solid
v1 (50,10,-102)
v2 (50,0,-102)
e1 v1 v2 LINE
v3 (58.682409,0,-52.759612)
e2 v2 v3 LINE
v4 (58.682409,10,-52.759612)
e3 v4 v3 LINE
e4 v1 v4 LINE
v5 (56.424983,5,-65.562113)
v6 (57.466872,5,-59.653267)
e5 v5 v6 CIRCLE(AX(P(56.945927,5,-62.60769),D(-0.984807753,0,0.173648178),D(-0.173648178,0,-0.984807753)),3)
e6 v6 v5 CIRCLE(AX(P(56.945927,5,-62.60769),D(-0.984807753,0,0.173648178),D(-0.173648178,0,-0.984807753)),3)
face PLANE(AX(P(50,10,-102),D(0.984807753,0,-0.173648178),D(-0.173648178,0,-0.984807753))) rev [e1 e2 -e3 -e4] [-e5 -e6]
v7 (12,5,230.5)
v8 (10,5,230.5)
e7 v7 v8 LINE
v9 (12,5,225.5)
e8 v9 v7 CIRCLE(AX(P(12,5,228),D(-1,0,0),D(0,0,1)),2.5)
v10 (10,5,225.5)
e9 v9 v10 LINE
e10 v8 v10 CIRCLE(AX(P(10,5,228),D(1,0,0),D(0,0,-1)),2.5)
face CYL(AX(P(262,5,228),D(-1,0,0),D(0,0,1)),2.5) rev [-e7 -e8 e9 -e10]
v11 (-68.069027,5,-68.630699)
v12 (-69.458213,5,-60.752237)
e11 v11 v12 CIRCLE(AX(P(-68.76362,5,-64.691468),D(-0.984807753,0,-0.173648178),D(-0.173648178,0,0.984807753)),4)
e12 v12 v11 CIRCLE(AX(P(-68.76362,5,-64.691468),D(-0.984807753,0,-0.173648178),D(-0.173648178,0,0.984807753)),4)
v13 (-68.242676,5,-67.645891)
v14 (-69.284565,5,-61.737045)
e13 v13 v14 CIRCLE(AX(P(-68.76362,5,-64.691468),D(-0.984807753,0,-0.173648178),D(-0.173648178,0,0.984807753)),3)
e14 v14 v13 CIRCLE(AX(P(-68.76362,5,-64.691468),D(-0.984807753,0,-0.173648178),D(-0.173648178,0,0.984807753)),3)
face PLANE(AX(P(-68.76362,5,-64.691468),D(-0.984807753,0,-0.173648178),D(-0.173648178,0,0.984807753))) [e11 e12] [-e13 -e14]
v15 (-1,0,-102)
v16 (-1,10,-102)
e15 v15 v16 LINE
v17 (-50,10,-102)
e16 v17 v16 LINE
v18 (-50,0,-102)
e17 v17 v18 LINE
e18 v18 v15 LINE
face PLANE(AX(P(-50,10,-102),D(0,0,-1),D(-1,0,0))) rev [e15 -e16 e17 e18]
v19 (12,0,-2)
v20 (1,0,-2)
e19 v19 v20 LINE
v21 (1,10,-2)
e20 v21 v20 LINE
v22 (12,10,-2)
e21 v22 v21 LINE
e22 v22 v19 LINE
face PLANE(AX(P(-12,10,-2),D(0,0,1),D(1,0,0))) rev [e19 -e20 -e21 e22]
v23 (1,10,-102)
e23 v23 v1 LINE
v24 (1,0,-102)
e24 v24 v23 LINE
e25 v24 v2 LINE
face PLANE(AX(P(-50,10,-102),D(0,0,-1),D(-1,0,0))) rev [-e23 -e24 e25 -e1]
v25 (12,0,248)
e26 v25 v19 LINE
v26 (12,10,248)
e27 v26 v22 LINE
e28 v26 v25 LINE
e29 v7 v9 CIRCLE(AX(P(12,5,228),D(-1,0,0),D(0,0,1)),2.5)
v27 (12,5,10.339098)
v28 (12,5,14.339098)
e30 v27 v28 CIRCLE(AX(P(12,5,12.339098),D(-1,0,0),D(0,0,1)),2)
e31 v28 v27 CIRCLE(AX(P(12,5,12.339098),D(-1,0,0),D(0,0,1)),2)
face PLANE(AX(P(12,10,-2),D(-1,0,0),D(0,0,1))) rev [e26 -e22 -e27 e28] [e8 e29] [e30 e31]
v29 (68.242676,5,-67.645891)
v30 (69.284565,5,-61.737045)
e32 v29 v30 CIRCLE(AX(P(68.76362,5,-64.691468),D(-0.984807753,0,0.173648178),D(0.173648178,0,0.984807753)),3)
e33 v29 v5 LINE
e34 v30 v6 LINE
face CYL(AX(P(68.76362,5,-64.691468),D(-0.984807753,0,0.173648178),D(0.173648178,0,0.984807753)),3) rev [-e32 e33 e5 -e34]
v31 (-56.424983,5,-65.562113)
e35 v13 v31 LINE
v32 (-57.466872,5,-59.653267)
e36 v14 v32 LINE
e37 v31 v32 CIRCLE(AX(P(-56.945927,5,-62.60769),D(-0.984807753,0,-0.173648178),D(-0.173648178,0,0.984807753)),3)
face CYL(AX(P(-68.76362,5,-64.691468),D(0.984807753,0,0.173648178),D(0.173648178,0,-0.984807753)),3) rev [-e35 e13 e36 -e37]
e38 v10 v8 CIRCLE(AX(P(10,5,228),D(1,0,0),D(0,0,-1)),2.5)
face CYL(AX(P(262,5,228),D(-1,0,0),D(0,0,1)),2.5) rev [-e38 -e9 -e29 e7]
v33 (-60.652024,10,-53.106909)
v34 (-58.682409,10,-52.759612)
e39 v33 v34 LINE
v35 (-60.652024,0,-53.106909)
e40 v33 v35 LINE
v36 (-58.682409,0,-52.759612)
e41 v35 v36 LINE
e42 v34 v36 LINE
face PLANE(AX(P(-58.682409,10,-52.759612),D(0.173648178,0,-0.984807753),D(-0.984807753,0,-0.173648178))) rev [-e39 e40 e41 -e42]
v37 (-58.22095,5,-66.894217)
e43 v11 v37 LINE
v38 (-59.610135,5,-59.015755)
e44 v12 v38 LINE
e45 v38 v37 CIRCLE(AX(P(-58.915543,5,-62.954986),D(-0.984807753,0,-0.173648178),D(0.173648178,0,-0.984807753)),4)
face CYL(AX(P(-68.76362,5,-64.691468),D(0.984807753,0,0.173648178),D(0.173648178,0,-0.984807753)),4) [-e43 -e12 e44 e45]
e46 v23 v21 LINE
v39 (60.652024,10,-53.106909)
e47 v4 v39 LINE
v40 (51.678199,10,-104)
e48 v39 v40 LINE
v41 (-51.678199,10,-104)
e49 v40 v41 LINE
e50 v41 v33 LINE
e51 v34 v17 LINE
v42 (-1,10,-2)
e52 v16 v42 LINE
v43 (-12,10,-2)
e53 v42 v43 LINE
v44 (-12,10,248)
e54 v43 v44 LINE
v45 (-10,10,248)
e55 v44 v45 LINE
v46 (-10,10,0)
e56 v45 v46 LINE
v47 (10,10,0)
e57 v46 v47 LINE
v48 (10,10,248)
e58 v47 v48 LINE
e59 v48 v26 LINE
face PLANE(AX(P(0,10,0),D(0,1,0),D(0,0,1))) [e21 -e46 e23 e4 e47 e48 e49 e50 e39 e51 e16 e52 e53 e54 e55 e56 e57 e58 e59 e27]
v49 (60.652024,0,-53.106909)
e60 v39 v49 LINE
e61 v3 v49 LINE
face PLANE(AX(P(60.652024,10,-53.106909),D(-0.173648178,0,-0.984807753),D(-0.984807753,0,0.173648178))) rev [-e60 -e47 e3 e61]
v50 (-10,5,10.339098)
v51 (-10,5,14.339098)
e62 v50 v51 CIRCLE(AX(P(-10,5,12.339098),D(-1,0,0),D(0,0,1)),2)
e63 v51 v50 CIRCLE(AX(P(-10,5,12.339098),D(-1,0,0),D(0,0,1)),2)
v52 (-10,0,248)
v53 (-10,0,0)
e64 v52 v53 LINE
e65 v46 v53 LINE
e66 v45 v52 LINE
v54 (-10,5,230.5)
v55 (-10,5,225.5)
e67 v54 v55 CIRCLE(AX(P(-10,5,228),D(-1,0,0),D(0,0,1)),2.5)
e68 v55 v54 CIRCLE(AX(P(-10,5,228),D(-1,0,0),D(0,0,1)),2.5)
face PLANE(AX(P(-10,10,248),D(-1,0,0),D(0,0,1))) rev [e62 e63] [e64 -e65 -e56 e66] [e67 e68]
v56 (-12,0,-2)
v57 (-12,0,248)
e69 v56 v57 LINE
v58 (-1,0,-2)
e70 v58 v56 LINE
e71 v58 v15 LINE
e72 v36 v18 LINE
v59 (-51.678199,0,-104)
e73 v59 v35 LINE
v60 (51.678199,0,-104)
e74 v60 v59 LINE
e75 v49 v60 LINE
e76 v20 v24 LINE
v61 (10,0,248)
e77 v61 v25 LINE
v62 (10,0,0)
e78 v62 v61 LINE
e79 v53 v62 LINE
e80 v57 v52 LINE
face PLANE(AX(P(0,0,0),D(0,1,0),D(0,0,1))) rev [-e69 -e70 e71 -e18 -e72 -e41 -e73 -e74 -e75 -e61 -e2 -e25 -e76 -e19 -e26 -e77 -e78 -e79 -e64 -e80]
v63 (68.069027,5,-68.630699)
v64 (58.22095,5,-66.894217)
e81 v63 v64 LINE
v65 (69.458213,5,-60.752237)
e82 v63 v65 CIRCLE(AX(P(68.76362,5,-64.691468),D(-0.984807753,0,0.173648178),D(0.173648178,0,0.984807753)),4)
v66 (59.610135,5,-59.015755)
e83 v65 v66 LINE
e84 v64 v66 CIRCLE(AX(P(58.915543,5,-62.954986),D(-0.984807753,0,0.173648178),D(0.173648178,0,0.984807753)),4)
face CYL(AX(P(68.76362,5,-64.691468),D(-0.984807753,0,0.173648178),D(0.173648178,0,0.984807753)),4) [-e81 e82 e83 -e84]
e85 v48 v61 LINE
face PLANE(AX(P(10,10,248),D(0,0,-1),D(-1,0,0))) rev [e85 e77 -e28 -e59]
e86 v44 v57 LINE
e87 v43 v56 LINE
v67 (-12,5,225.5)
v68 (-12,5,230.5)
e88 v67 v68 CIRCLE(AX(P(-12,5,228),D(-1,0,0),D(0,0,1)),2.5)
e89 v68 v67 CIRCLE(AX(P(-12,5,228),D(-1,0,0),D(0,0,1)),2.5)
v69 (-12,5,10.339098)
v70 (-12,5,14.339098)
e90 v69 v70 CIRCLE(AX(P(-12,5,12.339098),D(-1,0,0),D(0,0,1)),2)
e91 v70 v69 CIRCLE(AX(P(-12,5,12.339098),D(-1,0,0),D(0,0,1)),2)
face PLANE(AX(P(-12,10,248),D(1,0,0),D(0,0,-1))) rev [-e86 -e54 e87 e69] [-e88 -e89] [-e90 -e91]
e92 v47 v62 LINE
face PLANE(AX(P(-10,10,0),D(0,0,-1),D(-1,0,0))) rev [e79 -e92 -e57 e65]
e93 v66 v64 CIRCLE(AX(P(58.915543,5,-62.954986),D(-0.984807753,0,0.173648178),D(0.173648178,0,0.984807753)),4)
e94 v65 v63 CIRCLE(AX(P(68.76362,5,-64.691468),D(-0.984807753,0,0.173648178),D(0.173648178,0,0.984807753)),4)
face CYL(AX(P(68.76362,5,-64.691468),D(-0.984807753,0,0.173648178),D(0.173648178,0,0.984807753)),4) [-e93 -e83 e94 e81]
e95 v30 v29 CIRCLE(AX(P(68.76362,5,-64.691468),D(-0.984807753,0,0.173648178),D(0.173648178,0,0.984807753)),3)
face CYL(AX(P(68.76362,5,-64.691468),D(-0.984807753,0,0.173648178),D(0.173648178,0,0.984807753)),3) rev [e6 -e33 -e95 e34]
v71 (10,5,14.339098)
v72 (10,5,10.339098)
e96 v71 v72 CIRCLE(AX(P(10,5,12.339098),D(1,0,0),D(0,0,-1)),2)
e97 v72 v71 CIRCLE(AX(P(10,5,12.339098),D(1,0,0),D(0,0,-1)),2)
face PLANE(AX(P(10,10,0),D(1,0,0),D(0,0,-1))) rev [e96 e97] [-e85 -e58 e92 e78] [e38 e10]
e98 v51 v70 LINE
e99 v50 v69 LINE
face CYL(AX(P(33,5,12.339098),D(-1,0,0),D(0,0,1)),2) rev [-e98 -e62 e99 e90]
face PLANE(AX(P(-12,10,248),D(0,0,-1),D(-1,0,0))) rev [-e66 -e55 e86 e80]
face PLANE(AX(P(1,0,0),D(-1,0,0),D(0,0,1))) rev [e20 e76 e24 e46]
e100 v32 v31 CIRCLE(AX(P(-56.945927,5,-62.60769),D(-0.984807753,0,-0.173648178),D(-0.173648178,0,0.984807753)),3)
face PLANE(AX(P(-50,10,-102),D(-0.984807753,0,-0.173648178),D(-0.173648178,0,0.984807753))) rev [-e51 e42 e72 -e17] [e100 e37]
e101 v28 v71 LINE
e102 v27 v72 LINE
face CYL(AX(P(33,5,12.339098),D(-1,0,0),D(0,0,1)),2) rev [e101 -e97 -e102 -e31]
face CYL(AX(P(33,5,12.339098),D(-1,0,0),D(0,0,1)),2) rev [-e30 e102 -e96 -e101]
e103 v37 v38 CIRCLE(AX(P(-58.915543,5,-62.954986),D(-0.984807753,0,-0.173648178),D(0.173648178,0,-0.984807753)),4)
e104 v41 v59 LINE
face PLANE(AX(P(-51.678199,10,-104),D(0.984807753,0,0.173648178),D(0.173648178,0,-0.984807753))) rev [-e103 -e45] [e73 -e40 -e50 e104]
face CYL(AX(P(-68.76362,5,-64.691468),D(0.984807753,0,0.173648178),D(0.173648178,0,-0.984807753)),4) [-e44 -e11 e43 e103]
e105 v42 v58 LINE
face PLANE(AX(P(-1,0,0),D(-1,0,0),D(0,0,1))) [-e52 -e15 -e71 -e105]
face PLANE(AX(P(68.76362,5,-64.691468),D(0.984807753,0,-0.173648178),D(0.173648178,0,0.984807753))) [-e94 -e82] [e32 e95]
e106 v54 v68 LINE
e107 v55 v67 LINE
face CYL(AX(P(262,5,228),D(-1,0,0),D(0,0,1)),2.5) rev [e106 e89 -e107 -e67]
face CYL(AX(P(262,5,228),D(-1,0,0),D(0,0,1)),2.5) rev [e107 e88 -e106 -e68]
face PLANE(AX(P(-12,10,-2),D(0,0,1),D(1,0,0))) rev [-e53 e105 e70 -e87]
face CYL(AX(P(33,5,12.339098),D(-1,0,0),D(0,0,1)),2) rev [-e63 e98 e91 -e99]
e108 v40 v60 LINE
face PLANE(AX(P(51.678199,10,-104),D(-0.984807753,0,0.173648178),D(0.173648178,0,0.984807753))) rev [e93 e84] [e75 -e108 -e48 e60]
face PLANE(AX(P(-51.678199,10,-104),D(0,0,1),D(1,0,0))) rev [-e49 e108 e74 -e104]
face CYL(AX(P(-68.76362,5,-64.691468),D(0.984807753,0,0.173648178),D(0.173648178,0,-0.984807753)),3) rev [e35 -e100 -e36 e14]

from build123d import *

# Parameters (mm, degrees)
EXTRUDE_1_DEPTH     = 10
SKETCH_3_W          = 100
SKETCH_3_H          = 10
EXTRUDE_2_DEPTH     = 1
EXTRUDE_3_DEPTH     = 10
SKETCH_6_R          = 4
SKETCH_6_R_2        = 3
EXTRUDE_4_DEPTH     = 10
CUT_EXTRUDE_START   = -20
SKETCH_7_R          = 3
CUT_EXTRUDE_1_DEPTH = 20
SKETCH_9_R          = 2.5
CUT_EXTRUDE_2_DEPTH = 274
SKETCH_10_R         = 2
CUT_EXTRUDE_3_DEPTH = 45


with BuildPart() as part:
    # 草图1 → 凸台-拉伸1 (new body)
    with BuildSketch(Plane(origin=(0, 0, 0), x_dir=(1, 0, 0), z_dir=(0, 1, 0))):
        Polygon((-10, -248), (-10, 0), (10, 0), (10, -248), (12, -248), (12, 2), (-12, 2), (-12, -248), align=None)
    extrude(amount=EXTRUDE_1_DEPTH)

    # 草图3 → 凸台-拉伸2 (add, symmetric)
    with BuildSketch(Plane(origin=(0, 0, 0), x_dir=(0, 0, -1), z_dir=(1, 0, 0))):
        with Locations((52, 5)):
            Rectangle(SKETCH_3_W, SKETCH_3_H)
    extrude(amount=EXTRUDE_2_DEPTH, both=True)

    # 草图4 → 凸台-拉伸3 (add)
    with BuildSketch(Plane(origin=(0, 0, 0), x_dir=(1, 0, 0), z_dir=(0, 1, 0))):
        Polygon((-50, 102), (50, 102), (58.682408883, 52.759612349), (60.652024389, 53.106908705), (51.678199262, 104), (-51.678199262, 104), (-60.652024389, 53.106908705), (-58.682408883, 52.759612349), align=None)
    extrude(amount=EXTRUDE_3_DEPTH)

    # 草图6 → 凸台-拉伸4 (add)
    with BuildSketch(Plane(origin=(-67.904958335, 0, -11.973476278), x_dir=(-0.17364817766693408, 0, 0.9848077530122076), z_dir=(-0.9848077530122076, 0, -0.17364817766693408))):
        with Locations(Location((-51.767981924, 5, 0), (0, 0, 180))):
            Circle(SKETCH_6_R)
        with Locations((-51.767981924, 5)):
            Circle(SKETCH_6_R_2, mode=Mode.SUBTRACT)
    extrude_4 = extrude(amount=EXTRUDE_4_DEPTH)

    # 草图7 → 切除-拉伸1 (cut)
    with BuildSketch(Plane(origin=(-67.904958335, 0, -11.973476278), x_dir=(-0.17364817766693408, 0, 0.9848077530122076), z_dir=(-0.9848077530122076, 0, -0.17364817766693408)).offset(CUT_EXTRUDE_START)):
        with Locations((-51.767981924, 5)):
            Circle(SKETCH_7_R)
    cut_extrude_1 = extrude(amount=CUT_EXTRUDE_1_DEPTH, mode=Mode.SUBTRACT)

    # 镜向1: 凸台-拉伸4, 切除-拉伸1 across plane
    add(extrude_4.mirror(Plane(origin=(0, 0, 0), x_dir=(0, 0, 1), z_dir=(1, 0, 0))))
    add(cut_extrude_1.mirror(Plane(origin=(0, 0, 0), x_dir=(0, 0, 1), z_dir=(1, 0, 0))), mode=Mode.SUBTRACT)

    # 草图9 → 切除-拉伸2 (cut)
    with BuildSketch(Plane.ZY.offset(12)):
        with Locations((228, 5)):
            Circle(SKETCH_9_R)
    extrude(amount=-CUT_EXTRUDE_2_DEPTH, mode=Mode.SUBTRACT)

    # 草图10 → 切除-拉伸3 (cut)
    with BuildSketch(Plane.ZY.offset(12)):
        with Locations((12.339097651, 5)):
            Circle(SKETCH_10_R)
    extrude(amount=-CUT_EXTRUDE_3_DEPTH, mode=Mode.SUBTRACT)


solid = part.part
